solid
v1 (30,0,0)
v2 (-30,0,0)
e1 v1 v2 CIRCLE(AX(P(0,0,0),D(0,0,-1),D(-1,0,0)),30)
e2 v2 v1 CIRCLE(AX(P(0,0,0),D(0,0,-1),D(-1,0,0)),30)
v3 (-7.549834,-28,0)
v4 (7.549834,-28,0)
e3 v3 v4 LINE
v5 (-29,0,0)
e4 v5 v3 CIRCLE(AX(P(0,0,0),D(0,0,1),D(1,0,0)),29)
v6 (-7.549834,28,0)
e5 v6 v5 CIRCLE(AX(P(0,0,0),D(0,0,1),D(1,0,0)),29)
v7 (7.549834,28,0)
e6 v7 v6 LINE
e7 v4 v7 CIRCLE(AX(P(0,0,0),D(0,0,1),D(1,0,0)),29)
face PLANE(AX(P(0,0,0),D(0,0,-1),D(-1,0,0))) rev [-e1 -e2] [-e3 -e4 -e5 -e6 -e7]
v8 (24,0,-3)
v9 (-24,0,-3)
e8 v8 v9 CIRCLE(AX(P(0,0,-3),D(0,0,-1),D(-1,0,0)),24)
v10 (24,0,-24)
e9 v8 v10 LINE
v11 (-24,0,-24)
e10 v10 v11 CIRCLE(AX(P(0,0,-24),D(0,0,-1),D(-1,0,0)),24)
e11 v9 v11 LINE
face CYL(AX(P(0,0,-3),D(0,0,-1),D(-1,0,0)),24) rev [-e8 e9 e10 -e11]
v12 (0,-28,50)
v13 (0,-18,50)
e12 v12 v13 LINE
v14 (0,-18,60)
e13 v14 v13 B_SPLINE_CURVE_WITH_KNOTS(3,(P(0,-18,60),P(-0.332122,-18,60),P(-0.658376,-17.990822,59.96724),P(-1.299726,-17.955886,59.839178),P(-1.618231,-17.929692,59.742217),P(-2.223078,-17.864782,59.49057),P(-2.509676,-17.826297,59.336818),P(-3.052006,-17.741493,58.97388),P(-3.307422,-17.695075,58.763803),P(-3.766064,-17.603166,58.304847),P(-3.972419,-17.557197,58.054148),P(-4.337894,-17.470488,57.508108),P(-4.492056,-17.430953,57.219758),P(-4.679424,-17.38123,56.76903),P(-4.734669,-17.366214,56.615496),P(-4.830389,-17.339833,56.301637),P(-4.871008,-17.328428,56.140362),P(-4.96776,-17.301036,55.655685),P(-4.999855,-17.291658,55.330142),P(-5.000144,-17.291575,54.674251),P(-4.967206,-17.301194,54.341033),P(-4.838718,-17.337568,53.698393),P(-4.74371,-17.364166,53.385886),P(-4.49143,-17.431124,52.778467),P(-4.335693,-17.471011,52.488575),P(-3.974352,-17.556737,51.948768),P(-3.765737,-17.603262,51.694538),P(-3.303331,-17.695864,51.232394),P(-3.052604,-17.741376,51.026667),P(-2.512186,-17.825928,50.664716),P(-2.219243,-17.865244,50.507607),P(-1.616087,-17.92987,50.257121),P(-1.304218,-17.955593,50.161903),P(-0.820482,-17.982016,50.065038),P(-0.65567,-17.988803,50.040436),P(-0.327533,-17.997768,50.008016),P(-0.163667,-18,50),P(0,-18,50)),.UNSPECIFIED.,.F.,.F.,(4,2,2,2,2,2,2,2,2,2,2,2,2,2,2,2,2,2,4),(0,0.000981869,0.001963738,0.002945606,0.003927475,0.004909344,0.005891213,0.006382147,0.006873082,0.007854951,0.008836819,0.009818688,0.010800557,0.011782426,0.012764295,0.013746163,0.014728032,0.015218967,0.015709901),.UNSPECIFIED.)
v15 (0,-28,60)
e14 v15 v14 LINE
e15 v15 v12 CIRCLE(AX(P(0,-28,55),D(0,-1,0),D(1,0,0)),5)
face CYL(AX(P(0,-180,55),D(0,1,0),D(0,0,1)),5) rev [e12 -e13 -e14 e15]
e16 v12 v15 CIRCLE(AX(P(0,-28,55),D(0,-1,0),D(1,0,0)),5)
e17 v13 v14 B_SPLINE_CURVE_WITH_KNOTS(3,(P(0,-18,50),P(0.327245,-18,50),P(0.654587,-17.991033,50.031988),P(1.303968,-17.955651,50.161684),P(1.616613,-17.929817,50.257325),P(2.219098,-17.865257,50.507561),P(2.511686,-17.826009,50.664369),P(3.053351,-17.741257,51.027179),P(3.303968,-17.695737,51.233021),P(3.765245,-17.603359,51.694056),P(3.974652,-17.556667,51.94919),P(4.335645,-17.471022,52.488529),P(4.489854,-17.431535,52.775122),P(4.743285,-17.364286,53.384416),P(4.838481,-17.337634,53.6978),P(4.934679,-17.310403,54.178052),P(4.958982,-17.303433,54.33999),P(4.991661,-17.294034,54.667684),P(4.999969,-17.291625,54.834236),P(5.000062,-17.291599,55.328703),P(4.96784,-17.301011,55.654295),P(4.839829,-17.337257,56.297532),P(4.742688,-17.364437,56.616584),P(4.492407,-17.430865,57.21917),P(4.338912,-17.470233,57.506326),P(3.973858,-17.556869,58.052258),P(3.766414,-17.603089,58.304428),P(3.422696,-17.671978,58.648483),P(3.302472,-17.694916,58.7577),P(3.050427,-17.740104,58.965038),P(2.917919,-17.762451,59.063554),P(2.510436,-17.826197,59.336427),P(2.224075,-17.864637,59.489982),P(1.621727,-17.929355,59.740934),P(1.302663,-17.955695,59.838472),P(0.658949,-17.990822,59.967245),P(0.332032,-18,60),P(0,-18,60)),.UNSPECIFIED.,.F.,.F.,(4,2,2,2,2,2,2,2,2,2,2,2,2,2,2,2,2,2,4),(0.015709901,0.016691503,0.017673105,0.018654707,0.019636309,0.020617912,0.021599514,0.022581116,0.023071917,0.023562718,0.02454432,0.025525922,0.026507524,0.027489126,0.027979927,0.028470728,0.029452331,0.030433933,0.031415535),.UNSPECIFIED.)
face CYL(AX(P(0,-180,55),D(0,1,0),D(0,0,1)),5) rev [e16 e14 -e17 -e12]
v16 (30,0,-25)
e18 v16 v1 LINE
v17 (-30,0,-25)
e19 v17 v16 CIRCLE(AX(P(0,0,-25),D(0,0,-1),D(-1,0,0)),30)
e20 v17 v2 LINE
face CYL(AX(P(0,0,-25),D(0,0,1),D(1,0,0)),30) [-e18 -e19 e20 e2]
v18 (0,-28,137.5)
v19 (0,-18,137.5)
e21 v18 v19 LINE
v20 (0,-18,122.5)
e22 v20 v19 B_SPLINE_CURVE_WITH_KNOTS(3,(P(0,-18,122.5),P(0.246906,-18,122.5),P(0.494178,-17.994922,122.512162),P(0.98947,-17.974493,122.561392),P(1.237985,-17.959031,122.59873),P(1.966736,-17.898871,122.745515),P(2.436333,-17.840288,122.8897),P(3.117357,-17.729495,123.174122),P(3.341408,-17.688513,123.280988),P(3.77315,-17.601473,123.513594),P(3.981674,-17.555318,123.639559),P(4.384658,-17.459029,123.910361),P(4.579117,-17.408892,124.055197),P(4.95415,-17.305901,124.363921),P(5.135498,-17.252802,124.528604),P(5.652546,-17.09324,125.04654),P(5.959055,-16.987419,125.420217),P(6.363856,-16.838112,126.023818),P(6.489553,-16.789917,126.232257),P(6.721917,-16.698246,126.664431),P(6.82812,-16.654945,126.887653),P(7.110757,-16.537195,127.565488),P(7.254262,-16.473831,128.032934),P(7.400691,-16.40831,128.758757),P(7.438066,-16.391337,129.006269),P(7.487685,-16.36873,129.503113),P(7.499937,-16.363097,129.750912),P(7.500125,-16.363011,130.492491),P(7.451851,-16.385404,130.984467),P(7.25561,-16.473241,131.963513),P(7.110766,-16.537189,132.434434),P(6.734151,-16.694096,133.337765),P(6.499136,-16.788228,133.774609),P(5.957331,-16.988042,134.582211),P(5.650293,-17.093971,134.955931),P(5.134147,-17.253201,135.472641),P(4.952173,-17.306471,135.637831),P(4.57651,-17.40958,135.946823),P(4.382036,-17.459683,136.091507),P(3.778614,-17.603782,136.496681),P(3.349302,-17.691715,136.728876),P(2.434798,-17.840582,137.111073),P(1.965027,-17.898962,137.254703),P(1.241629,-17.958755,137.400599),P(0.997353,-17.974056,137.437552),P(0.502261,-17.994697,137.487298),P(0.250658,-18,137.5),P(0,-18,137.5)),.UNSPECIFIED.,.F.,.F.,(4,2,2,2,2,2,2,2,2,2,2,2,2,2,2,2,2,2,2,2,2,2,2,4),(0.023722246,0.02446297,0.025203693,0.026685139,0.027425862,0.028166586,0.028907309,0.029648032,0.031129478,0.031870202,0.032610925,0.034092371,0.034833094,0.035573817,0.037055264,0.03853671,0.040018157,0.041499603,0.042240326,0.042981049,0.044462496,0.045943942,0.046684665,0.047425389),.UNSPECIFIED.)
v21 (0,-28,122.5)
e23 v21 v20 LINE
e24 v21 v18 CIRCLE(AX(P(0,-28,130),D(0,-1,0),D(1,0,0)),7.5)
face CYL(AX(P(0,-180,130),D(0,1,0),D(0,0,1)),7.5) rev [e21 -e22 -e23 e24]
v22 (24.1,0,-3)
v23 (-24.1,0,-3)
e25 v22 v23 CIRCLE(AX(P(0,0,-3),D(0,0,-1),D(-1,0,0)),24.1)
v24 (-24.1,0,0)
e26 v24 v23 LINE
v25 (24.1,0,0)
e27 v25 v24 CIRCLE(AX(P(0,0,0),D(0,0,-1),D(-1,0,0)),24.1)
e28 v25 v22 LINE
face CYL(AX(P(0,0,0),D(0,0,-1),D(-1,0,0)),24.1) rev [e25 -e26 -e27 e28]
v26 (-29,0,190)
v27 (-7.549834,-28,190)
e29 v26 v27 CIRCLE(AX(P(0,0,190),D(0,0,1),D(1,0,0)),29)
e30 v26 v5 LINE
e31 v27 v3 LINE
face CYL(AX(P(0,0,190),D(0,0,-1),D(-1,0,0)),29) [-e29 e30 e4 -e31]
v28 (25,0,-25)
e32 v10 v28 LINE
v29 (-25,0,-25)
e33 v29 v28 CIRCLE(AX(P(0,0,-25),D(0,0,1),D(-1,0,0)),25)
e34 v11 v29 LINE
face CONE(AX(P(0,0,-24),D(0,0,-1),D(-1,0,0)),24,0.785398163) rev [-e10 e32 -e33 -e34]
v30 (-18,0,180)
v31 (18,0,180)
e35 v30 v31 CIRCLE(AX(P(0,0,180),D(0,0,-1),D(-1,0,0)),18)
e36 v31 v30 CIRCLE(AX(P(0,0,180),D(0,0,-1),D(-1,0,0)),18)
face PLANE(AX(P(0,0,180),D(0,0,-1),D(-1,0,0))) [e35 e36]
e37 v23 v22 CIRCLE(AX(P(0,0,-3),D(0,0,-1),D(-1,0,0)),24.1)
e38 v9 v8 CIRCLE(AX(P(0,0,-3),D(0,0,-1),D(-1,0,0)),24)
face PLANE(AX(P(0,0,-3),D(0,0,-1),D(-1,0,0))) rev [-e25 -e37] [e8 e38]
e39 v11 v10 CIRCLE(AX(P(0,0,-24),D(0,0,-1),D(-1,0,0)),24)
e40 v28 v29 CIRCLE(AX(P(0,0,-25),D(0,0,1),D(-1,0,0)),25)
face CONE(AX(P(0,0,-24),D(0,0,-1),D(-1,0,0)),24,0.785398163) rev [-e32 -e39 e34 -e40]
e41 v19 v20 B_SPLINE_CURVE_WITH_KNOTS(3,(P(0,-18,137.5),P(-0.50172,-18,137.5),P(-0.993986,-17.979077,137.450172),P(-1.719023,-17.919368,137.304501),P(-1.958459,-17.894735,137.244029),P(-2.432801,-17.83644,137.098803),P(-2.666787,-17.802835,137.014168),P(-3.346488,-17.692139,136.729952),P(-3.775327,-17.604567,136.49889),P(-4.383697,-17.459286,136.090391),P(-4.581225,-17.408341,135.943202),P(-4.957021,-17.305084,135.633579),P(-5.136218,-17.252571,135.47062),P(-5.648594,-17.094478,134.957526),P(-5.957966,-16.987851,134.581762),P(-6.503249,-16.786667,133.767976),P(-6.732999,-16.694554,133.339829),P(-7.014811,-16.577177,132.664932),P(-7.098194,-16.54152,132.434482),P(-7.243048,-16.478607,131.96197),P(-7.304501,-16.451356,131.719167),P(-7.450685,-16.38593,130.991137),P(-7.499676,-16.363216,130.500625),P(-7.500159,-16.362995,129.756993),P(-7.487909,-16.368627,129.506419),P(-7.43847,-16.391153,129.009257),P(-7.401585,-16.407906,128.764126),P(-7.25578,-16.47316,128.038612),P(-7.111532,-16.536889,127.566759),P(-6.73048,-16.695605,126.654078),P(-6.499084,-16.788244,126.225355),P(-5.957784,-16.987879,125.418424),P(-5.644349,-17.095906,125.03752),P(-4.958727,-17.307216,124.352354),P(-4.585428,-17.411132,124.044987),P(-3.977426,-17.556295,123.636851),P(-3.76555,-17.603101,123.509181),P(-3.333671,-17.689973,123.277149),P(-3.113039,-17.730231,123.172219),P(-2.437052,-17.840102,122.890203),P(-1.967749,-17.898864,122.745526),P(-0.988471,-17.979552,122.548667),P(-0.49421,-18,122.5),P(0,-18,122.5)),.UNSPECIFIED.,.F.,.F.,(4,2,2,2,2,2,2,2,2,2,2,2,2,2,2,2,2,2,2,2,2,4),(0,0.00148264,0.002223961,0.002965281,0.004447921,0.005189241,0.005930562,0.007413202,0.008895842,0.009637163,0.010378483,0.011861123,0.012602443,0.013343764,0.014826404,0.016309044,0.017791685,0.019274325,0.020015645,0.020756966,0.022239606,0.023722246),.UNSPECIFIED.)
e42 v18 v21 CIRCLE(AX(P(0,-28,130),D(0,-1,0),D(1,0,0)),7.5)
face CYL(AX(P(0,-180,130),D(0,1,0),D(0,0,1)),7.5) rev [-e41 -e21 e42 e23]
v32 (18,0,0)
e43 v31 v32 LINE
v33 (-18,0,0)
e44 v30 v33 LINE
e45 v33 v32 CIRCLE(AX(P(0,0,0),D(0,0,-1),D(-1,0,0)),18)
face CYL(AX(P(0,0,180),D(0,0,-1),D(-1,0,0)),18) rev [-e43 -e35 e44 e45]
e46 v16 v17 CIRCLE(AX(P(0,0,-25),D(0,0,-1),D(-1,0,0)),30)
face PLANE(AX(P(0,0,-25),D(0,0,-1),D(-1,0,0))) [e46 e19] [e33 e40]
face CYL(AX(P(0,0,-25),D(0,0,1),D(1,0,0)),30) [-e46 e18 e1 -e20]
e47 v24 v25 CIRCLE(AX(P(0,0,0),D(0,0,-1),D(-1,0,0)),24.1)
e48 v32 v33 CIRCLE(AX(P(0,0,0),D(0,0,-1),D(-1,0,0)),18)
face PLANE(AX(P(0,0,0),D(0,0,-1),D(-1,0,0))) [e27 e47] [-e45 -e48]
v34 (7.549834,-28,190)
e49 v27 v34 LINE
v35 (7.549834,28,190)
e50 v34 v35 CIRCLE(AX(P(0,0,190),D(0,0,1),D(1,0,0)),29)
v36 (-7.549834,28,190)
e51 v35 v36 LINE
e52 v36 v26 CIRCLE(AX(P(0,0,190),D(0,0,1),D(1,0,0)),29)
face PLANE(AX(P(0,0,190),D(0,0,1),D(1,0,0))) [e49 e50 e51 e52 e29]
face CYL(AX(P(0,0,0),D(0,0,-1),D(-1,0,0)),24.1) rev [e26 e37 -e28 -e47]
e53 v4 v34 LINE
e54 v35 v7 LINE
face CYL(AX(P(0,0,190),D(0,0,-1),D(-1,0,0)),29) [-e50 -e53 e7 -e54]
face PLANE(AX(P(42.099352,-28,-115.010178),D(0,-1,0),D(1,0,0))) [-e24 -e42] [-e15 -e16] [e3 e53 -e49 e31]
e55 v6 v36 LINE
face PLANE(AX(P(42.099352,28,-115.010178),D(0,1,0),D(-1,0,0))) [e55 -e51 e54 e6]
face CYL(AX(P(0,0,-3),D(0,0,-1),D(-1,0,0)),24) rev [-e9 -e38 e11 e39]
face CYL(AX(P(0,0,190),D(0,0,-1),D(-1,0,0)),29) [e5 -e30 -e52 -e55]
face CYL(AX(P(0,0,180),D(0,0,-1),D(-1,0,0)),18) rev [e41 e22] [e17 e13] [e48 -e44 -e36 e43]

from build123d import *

# Parameters (mm, degrees)
SKETCH1_R           = 29
BOSS_EXTRUDE1_DEPTH = 190
SKETCH2_R           = 30
BOSS_EXTRUDE2_DEPTH = 25
SKETCH4_OUTSIDE_W   = 108.228
SKETCH4_OUTSIDE_H   = 108.228
SKETCH4_OUTSIDE_W_2 = 84.198703348
SKETCH4_OUTSIDE_H_2 = 56
CUT_EXTRUDE1_DEPTH  = 190
SKETCH5_R           = 24
CUT_EXTRUDE2_DEPTH  = 22
SKETCH6_R           = 24.1
CUT_EXTRUDE3_DEPTH  = 3
SKETCH7_R           = 18
CUT_EXTRUDE4_DEPTH  = 180
SKETCH8_R           = 5
SKETCH8_R_2         = 7.5
CUT_EXTRUDE5_DEPTH  = 180
CHAMFER1_SIZE       = 1


with BuildPart() as part:
    # Sketch1 → Boss-Extrude1 (new body)
    with BuildSketch(Plane.XY):
        Circle(SKETCH1_R)
    extrude(amount=BOSS_EXTRUDE1_DEPTH)

    # Sketch2 → Boss-Extrude2 (add)
    with BuildSketch(Plane(origin=(0, 0, 0), x_dir=(-1, 0, 0), z_dir=(0, 0, -1))):
        Circle(SKETCH2_R)
    extrude(amount=BOSS_EXTRUDE2_DEPTH)

    # Sketch4 outside → Cut-Extrude1 (cut)
    with BuildSketch(Plane.XY.offset(190)):
        Rectangle(SKETCH4_OUTSIDE_W, SKETCH4_OUTSIDE_H)
        Rectangle(SKETCH4_OUTSIDE_W_2, SKETCH4_OUTSIDE_H_2, mode=Mode.SUBTRACT)
    extrude(amount=-CUT_EXTRUDE1_DEPTH, mode=Mode.SUBTRACT)

    # Sketch5 → Cut-Extrude2 (cut)
    with BuildSketch(Plane(origin=(0, 0, -25), x_dir=(-1, 0, 0), z_dir=(0, 0, -1))):
        Circle(SKETCH5_R)
    extrude(amount=-CUT_EXTRUDE2_DEPTH, mode=Mode.SUBTRACT)

    # Sketch6 → Cut-Extrude3 (cut)
    with BuildSketch(Plane(origin=(0, 0, -3), x_dir=(-1, 0, 0), z_dir=(0, 0, -1))):
        Circle(SKETCH6_R)
    extrude(amount=-CUT_EXTRUDE3_DEPTH, mode=Mode.SUBTRACT)

    # Sketch7 → Cut-Extrude4 (cut)
    with BuildSketch(Plane(origin=(0, 0, 0), x_dir=(-1, 0, 0), z_dir=(0, 0, -1))):
        Circle(SKETCH7_R)
    extrude(amount=-CUT_EXTRUDE4_DEPTH, mode=Mode.SUBTRACT)

    # Sketch8 → Cut-Extrude5 (cut)
    with BuildSketch(Plane(origin=(0, 0, 0), x_dir=(1, 0, 0), z_dir=(0, 1, 0))):
        with Locations(Location((0, -55, 0), (0, 0, 270))):
            Circle(SKETCH8_R)
        with Locations(Location((0, -130, 0), (0, 0, 270))):
            Circle(SKETCH8_R_2)
    extrude(amount=-CUT_EXTRUDE5_DEPTH, mode=Mode.SUBTRACT)

    # Chamfer1
    chamfer1_edges = [part.edges().sort_by_distance(p)[0] for p in [
        (24, 0, -25),
    ]]
    chamfer(chamfer1_edges, length=CHAMFER1_SIZE)


solid = part.part
